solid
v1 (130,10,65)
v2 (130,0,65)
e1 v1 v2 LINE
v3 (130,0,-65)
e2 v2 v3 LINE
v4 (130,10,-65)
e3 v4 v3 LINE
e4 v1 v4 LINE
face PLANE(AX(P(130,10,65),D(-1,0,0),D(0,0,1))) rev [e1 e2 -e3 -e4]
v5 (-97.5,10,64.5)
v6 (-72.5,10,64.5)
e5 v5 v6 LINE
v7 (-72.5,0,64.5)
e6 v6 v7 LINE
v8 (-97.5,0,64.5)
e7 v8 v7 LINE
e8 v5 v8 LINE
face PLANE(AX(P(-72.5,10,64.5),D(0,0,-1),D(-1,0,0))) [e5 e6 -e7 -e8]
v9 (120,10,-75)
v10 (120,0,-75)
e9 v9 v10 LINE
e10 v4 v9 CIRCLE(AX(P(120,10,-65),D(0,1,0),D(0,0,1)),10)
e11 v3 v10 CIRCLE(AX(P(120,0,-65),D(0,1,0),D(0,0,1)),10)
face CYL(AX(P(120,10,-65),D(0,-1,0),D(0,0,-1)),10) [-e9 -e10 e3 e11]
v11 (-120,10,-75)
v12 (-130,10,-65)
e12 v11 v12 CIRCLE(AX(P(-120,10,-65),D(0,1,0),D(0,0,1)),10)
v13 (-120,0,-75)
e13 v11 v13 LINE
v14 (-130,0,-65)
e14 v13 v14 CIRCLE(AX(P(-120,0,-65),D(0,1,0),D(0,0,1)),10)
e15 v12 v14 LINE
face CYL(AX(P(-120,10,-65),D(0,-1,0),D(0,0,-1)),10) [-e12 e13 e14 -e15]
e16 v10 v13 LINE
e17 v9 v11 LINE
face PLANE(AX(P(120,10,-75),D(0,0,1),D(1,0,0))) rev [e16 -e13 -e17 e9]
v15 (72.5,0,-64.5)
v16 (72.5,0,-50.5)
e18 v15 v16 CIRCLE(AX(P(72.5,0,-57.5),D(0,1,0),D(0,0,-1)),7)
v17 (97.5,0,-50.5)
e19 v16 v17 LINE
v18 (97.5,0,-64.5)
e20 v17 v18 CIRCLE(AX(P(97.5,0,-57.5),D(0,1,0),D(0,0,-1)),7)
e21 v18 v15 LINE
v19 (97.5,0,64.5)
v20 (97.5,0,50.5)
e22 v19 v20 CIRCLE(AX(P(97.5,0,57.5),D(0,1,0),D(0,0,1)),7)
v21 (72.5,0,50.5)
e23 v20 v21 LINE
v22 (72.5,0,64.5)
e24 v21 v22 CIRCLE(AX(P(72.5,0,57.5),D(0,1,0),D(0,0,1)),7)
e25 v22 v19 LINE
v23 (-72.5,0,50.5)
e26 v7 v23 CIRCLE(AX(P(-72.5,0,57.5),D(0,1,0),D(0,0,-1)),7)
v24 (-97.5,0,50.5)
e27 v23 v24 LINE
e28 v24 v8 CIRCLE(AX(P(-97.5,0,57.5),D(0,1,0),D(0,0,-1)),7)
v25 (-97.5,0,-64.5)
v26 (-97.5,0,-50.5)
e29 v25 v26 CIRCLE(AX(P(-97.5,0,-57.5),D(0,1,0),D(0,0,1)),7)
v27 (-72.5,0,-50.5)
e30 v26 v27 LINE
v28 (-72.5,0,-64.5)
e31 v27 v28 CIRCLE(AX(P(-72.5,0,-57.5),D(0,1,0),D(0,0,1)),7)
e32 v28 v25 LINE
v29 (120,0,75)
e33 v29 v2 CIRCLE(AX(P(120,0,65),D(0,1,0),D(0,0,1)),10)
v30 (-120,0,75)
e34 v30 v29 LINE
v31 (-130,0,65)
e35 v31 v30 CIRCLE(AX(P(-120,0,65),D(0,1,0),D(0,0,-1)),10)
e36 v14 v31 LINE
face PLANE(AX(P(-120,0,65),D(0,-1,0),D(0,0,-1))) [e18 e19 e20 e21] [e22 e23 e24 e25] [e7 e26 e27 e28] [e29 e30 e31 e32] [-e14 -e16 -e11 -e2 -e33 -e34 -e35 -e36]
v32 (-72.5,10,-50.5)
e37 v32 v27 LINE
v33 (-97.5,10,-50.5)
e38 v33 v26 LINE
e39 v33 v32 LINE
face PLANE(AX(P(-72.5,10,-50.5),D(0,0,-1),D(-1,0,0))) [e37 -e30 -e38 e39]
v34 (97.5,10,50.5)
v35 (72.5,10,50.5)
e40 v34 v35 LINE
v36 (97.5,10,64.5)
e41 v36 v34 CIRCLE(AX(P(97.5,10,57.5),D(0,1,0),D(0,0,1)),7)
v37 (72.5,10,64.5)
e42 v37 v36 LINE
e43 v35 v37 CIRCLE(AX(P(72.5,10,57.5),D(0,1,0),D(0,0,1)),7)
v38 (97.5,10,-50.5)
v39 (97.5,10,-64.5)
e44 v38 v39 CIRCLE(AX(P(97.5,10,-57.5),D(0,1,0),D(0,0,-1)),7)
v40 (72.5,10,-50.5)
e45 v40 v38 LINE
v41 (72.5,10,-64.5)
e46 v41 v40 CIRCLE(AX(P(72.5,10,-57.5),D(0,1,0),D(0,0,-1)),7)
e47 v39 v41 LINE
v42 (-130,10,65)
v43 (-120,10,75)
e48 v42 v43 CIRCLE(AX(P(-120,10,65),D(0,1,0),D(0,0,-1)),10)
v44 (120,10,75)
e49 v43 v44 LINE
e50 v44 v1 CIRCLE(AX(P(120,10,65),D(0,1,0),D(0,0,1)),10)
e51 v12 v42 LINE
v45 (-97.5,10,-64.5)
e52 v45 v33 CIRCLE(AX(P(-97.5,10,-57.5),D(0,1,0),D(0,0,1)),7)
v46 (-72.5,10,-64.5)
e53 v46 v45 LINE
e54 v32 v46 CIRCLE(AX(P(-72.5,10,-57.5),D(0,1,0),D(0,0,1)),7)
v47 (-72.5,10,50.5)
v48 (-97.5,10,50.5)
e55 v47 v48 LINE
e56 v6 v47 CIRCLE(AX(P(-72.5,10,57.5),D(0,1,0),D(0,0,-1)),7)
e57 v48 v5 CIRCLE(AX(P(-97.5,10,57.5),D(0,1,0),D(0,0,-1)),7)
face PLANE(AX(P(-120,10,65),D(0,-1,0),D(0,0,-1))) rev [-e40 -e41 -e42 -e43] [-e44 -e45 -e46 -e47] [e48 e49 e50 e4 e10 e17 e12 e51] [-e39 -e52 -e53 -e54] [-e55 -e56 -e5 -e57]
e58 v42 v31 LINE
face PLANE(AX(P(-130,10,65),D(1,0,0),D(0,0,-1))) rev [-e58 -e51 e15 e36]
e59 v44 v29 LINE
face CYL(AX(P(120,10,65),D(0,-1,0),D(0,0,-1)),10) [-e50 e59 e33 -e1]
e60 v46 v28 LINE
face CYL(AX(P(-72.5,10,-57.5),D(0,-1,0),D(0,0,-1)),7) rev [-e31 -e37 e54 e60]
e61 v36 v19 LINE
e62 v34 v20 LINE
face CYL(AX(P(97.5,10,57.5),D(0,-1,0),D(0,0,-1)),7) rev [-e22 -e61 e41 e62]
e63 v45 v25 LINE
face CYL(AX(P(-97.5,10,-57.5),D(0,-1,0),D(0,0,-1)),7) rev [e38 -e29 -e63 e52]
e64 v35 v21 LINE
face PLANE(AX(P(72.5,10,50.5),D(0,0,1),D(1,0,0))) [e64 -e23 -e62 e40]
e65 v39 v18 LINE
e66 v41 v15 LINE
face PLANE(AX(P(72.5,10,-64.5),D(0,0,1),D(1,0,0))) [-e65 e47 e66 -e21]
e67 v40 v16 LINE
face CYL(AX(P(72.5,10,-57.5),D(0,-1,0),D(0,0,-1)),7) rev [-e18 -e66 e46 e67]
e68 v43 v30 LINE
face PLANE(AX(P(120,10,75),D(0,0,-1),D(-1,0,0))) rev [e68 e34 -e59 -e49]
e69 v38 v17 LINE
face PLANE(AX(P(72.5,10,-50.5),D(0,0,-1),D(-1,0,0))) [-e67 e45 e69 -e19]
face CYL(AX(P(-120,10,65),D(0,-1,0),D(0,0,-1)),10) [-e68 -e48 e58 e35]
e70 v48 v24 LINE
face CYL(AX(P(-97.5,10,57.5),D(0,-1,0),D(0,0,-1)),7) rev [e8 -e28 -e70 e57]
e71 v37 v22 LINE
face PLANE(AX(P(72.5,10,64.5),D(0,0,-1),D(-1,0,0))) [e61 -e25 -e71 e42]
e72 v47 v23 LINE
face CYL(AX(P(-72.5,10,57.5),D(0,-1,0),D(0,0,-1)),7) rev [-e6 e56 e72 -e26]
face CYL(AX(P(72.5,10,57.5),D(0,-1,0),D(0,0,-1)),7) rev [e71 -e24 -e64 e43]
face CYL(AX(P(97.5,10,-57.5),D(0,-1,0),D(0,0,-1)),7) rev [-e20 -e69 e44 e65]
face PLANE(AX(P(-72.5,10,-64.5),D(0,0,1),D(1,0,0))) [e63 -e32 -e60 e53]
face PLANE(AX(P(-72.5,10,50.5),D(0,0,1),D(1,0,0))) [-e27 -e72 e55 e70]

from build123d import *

# Parameters (mm, degrees)
EXTRUDE_1_DEPTH = 10


with BuildPart() as part:
    # 草图1 → 凸台-拉伸1 (new body)
    with BuildSketch(Plane(origin=(0, 0, 0), x_dir=(1, 0, 0), z_dir=(0, 1, 0))):
        with BuildLine():
            Line((120, -75), (-120, -75))
            ThreePointArc((-120, -75), (-127.071067812, -72.071067812), (-130, -65))
            Line((-130, -65), (-130, 65))
            ThreePointArc((-130, 65), (-127.071067812, 72.071067812), (-120, 75))
            Line((-120, 75), (120, 75))
            ThreePointArc((120, 75), (127.071067812, 72.071067812), (130, 65))
            Line((130, 65), (130, -65))
            ThreePointArc((130, -65), (127.071067812, -72.071067812), (120, -75))
        make_face()
        with BuildLine():
            Line((-72.5, 50.5), (-97.5, 50.5))
            ThreePointArc((-97.5, 50.5), (-104.5, 57.5), (-97.5, 64.5))
            Line((-97.5, 64.5), (-72.5, 64.5))
            ThreePointArc((-72.5, 64.5), (-65.5, 57.5), (-72.5, 50.5))
        make_face(mode=Mode.SUBTRACT)
        with BuildLine():
            Line((72.5, 50.5), (97.5, 50.5))
            ThreePointArc((97.5, 50.5), (104.5, 57.5), (97.5, 64.5))
            Line((97.5, 64.5), (72.5, 64.5))
            ThreePointArc((72.5, 64.5), (65.5, 57.5), (72.5, 50.5))
        make_face(mode=Mode.SUBTRACT)
        with BuildLine():
            Line((-72.5, -50.5), (-97.5, -50.5))
            ThreePointArc((-97.5, -50.5), (-104.5, -57.5), (-97.5, -64.5))
            Line((-97.5, -64.5), (-72.5, -64.5))
            ThreePointArc((-72.5, -64.5), (-65.5, -57.5), (-72.5, -50.5))
        make_face(mode=Mode.SUBTRACT)
        with BuildLine():
            Line((72.5, -50.5), (97.5, -50.5))
            ThreePointArc((97.5, -50.5), (104.5, -57.5), (97.5, -64.5))
            Line((97.5, -64.5), (72.5, -64.5))
            ThreePointArc((72.5, -64.5), (65.5, -57.5), (72.5, -50.5))
        make_face(mode=Mode.SUBTRACT)
    extrude(amount=EXTRUDE_1_DEPTH)


solid = part.part
